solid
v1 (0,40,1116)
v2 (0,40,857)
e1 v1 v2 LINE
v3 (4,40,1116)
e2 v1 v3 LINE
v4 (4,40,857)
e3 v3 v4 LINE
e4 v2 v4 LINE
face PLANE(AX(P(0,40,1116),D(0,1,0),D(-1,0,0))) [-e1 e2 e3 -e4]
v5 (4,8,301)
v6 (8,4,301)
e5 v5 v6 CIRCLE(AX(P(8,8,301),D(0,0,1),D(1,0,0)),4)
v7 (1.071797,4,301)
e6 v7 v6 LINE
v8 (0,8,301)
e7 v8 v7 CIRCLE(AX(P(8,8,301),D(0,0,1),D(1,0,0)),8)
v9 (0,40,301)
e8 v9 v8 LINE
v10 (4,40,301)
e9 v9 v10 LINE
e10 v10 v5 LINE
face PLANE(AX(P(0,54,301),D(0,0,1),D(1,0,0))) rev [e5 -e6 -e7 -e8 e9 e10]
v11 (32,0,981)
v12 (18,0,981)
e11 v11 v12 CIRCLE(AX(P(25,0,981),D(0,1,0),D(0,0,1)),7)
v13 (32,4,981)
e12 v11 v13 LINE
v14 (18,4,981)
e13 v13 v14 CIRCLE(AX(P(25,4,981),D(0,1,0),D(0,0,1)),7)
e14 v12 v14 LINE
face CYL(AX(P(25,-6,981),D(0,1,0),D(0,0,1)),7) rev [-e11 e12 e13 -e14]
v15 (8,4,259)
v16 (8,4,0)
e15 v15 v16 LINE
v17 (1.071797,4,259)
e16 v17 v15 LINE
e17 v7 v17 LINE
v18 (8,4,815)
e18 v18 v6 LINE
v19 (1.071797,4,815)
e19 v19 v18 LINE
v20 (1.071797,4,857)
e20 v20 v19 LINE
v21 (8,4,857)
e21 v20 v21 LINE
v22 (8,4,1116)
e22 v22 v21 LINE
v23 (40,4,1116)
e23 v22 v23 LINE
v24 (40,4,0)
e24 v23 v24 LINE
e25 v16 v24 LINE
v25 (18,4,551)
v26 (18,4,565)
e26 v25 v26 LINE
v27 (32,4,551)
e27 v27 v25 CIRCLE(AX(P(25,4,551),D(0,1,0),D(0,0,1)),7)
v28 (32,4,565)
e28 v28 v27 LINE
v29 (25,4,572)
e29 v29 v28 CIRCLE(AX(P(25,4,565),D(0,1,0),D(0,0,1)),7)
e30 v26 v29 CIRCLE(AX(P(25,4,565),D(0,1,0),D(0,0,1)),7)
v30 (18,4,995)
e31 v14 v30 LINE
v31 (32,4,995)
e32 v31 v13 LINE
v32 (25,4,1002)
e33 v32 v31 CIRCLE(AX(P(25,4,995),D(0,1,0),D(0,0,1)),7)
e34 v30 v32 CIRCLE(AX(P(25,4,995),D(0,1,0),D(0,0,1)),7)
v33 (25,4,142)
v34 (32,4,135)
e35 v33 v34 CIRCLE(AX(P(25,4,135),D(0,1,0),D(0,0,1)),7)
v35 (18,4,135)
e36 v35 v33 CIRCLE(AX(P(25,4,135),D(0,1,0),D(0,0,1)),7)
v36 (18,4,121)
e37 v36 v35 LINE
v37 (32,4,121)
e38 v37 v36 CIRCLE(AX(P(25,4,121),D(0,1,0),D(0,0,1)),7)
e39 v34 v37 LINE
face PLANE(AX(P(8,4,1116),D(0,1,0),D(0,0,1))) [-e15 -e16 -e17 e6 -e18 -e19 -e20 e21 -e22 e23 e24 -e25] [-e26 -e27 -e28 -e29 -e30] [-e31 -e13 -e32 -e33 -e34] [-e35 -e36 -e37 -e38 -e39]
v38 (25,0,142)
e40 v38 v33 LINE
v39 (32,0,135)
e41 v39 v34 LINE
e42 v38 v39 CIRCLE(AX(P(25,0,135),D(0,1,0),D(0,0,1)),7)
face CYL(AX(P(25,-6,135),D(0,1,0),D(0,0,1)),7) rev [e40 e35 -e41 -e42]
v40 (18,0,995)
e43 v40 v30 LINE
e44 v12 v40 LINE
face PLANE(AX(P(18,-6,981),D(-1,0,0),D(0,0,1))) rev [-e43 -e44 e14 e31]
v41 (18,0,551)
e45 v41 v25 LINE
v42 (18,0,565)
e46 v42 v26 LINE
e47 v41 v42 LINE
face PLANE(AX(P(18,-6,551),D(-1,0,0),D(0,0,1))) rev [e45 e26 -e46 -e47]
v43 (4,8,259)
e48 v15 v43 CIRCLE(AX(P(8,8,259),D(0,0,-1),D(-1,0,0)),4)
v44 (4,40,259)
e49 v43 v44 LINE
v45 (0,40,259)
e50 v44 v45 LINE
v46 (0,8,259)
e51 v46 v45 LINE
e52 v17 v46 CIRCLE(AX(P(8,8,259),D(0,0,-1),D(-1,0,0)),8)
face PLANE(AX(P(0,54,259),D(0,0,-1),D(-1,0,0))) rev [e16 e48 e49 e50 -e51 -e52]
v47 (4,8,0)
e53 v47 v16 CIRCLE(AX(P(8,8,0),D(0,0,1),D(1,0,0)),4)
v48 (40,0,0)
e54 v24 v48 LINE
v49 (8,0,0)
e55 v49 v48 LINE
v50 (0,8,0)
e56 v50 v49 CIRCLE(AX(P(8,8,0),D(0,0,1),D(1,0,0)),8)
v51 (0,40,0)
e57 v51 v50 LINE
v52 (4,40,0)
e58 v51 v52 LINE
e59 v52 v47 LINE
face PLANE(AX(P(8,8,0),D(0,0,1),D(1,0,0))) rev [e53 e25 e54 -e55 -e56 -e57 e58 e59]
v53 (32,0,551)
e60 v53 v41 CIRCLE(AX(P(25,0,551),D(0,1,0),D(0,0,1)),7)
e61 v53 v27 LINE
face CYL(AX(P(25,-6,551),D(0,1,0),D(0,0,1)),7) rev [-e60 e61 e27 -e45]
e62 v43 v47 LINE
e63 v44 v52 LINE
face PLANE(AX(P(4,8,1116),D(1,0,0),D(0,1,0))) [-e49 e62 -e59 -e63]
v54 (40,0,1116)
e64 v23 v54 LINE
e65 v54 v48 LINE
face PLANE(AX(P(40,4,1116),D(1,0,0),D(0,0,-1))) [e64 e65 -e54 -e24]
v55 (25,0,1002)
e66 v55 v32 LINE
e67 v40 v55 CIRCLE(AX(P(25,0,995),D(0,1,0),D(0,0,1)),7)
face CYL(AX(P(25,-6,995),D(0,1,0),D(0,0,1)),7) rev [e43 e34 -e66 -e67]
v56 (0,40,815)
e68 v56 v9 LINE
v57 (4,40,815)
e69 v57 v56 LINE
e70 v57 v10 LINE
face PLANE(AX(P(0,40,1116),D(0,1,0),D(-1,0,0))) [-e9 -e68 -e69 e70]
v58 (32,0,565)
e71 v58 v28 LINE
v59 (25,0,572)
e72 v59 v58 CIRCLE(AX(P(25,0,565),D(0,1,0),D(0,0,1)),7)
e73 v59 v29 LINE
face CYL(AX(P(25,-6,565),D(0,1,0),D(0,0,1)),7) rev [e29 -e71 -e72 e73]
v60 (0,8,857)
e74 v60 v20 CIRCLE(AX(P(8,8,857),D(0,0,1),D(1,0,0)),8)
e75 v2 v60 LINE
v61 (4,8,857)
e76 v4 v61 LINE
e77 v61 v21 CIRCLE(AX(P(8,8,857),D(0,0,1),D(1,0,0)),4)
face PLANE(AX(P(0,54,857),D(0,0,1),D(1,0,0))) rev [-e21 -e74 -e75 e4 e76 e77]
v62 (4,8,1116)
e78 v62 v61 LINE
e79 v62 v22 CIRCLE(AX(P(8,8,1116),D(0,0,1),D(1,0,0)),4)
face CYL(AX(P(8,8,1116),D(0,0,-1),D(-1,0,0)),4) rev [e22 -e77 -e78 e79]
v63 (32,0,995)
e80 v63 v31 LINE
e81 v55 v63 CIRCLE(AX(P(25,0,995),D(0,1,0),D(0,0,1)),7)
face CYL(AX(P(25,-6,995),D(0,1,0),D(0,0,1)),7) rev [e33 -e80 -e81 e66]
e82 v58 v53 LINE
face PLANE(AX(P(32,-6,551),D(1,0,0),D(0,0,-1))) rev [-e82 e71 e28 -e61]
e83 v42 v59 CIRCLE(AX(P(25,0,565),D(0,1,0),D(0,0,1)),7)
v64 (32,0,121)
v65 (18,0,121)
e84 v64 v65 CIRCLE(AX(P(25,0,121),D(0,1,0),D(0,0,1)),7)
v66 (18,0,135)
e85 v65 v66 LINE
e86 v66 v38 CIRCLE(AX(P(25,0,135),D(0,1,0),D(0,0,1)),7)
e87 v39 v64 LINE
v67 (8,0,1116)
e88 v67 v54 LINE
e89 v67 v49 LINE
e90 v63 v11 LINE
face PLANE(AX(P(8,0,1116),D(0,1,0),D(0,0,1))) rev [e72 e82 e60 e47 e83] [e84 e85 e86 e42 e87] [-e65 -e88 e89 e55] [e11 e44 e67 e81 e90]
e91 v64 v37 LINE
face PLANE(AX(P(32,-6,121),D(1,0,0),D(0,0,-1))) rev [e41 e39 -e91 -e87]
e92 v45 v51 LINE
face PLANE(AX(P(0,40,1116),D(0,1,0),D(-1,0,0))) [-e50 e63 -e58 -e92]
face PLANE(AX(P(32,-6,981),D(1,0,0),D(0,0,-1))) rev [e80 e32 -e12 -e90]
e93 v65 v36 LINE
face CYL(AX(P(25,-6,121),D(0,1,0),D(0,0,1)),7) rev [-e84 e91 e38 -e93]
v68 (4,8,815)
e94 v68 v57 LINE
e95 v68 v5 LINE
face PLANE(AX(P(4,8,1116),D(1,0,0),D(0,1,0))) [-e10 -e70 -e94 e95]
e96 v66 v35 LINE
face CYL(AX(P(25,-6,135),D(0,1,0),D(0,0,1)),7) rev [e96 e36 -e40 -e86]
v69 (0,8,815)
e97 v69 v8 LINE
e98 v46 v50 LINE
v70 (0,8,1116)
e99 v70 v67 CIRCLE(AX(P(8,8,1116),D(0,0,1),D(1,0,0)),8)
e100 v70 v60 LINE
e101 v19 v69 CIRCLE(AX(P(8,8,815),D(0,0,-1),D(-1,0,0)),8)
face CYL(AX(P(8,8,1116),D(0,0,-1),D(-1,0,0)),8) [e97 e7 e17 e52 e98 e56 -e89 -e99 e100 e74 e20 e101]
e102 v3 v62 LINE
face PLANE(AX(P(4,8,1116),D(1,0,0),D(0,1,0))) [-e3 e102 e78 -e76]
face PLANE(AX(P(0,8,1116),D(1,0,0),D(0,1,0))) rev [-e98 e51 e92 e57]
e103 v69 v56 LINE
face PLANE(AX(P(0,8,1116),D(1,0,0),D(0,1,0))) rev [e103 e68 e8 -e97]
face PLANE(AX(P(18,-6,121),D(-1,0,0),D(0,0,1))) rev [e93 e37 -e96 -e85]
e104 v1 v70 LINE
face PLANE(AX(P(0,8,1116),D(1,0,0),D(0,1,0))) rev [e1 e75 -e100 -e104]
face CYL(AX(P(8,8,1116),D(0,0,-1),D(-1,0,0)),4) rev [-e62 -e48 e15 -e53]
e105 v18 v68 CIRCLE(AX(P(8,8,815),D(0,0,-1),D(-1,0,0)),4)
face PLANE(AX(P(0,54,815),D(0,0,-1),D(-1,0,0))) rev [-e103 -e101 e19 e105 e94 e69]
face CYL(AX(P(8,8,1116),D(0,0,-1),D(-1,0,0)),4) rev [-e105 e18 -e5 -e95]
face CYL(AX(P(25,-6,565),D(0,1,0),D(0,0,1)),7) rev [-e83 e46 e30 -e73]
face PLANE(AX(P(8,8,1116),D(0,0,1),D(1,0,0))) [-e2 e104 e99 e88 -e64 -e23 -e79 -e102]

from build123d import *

# Parameters (mm, degrees)
EXTRUDE_THIN1_DEPTH = 1116
SKETCH2_W           = 42
SKETCH2_H           = 50
CUT_EXTRUDE1_DEPTH  = 1118.432772027
CUT_EXTRUDE2_DEPTH  = 10
LPATTERN1_COUNT     = 2
LPATTERN1_PITCH     = 430
LPATTERN2_COUNT     = 2
LPATTERN2_PITCH     = 430


with BuildPart() as part:
    # Sketch1 → Extrude-Thin1 (new body)
    with BuildSketch(Plane.XY):
        with BuildLine():
            Line((40, 0), (8, 0))
            ThreePointArc((8, 0), (2.343145751, 2.343145751), (0, 8))
            Line((0, 8), (0, 40))
            Line((0, 40), (4, 40))
            Line((4, 40), (4, 8))
            ThreePointArc((4, 8), (5.171572875, 5.171572875), (8, 4))
            Line((8, 4), (40, 4))
            Line((40, 4), (40, 0))
        make_face()
    extrude(amount=EXTRUDE_THIN1_DEPTH)

    # Sketch2 → Cut-Extrude1 (cut, through all)
    with BuildSketch(Plane(origin=(40, 0, 0), x_dir=(0, 0, -1), z_dir=(1, 0, 0))):
        with Locations((-280, 29)):
            Rectangle(SKETCH2_W, SKETCH2_H)
        with Locations((-836, 29)):
            Rectangle(SKETCH2_W, SKETCH2_H)
    extrude(amount=-CUT_EXTRUDE1_DEPTH, mode=Mode.SUBTRACT)

    # Sketch3 → Cut-Extrude2 (cut)
    with BuildSketch(Plane(origin=(0, 4, 0), x_dir=(1, 0, 0), z_dir=(0, 1, 0))):
        with BuildLine():
            Line((32, -551), (32, -565))
            ThreePointArc((32, -565), (25, -572), (18, -565))
            Line((18, -565), (18, -551))
            ThreePointArc((18, -551), (25, -544), (32, -551))
        make_face()
    cut_extrude2 = extrude(amount=-CUT_EXTRUDE2_DEPTH, mode=Mode.SUBTRACT)

    # LPattern1: Cut-Extrude2 ×2
    with Locations(*[(0, 0, -i * LPATTERN1_PITCH) for i in range(1, LPATTERN1_COUNT)]):
        add(cut_extrude2, mode=Mode.SUBTRACT)

    # LPattern2: Cut-Extrude2 ×2
    with Locations(*[(0, 0, i * LPATTERN2_PITCH) for i in range(1, LPATTERN2_COUNT)]):
        add(cut_extrude2, mode=Mode.SUBTRACT)


solid = part.part
